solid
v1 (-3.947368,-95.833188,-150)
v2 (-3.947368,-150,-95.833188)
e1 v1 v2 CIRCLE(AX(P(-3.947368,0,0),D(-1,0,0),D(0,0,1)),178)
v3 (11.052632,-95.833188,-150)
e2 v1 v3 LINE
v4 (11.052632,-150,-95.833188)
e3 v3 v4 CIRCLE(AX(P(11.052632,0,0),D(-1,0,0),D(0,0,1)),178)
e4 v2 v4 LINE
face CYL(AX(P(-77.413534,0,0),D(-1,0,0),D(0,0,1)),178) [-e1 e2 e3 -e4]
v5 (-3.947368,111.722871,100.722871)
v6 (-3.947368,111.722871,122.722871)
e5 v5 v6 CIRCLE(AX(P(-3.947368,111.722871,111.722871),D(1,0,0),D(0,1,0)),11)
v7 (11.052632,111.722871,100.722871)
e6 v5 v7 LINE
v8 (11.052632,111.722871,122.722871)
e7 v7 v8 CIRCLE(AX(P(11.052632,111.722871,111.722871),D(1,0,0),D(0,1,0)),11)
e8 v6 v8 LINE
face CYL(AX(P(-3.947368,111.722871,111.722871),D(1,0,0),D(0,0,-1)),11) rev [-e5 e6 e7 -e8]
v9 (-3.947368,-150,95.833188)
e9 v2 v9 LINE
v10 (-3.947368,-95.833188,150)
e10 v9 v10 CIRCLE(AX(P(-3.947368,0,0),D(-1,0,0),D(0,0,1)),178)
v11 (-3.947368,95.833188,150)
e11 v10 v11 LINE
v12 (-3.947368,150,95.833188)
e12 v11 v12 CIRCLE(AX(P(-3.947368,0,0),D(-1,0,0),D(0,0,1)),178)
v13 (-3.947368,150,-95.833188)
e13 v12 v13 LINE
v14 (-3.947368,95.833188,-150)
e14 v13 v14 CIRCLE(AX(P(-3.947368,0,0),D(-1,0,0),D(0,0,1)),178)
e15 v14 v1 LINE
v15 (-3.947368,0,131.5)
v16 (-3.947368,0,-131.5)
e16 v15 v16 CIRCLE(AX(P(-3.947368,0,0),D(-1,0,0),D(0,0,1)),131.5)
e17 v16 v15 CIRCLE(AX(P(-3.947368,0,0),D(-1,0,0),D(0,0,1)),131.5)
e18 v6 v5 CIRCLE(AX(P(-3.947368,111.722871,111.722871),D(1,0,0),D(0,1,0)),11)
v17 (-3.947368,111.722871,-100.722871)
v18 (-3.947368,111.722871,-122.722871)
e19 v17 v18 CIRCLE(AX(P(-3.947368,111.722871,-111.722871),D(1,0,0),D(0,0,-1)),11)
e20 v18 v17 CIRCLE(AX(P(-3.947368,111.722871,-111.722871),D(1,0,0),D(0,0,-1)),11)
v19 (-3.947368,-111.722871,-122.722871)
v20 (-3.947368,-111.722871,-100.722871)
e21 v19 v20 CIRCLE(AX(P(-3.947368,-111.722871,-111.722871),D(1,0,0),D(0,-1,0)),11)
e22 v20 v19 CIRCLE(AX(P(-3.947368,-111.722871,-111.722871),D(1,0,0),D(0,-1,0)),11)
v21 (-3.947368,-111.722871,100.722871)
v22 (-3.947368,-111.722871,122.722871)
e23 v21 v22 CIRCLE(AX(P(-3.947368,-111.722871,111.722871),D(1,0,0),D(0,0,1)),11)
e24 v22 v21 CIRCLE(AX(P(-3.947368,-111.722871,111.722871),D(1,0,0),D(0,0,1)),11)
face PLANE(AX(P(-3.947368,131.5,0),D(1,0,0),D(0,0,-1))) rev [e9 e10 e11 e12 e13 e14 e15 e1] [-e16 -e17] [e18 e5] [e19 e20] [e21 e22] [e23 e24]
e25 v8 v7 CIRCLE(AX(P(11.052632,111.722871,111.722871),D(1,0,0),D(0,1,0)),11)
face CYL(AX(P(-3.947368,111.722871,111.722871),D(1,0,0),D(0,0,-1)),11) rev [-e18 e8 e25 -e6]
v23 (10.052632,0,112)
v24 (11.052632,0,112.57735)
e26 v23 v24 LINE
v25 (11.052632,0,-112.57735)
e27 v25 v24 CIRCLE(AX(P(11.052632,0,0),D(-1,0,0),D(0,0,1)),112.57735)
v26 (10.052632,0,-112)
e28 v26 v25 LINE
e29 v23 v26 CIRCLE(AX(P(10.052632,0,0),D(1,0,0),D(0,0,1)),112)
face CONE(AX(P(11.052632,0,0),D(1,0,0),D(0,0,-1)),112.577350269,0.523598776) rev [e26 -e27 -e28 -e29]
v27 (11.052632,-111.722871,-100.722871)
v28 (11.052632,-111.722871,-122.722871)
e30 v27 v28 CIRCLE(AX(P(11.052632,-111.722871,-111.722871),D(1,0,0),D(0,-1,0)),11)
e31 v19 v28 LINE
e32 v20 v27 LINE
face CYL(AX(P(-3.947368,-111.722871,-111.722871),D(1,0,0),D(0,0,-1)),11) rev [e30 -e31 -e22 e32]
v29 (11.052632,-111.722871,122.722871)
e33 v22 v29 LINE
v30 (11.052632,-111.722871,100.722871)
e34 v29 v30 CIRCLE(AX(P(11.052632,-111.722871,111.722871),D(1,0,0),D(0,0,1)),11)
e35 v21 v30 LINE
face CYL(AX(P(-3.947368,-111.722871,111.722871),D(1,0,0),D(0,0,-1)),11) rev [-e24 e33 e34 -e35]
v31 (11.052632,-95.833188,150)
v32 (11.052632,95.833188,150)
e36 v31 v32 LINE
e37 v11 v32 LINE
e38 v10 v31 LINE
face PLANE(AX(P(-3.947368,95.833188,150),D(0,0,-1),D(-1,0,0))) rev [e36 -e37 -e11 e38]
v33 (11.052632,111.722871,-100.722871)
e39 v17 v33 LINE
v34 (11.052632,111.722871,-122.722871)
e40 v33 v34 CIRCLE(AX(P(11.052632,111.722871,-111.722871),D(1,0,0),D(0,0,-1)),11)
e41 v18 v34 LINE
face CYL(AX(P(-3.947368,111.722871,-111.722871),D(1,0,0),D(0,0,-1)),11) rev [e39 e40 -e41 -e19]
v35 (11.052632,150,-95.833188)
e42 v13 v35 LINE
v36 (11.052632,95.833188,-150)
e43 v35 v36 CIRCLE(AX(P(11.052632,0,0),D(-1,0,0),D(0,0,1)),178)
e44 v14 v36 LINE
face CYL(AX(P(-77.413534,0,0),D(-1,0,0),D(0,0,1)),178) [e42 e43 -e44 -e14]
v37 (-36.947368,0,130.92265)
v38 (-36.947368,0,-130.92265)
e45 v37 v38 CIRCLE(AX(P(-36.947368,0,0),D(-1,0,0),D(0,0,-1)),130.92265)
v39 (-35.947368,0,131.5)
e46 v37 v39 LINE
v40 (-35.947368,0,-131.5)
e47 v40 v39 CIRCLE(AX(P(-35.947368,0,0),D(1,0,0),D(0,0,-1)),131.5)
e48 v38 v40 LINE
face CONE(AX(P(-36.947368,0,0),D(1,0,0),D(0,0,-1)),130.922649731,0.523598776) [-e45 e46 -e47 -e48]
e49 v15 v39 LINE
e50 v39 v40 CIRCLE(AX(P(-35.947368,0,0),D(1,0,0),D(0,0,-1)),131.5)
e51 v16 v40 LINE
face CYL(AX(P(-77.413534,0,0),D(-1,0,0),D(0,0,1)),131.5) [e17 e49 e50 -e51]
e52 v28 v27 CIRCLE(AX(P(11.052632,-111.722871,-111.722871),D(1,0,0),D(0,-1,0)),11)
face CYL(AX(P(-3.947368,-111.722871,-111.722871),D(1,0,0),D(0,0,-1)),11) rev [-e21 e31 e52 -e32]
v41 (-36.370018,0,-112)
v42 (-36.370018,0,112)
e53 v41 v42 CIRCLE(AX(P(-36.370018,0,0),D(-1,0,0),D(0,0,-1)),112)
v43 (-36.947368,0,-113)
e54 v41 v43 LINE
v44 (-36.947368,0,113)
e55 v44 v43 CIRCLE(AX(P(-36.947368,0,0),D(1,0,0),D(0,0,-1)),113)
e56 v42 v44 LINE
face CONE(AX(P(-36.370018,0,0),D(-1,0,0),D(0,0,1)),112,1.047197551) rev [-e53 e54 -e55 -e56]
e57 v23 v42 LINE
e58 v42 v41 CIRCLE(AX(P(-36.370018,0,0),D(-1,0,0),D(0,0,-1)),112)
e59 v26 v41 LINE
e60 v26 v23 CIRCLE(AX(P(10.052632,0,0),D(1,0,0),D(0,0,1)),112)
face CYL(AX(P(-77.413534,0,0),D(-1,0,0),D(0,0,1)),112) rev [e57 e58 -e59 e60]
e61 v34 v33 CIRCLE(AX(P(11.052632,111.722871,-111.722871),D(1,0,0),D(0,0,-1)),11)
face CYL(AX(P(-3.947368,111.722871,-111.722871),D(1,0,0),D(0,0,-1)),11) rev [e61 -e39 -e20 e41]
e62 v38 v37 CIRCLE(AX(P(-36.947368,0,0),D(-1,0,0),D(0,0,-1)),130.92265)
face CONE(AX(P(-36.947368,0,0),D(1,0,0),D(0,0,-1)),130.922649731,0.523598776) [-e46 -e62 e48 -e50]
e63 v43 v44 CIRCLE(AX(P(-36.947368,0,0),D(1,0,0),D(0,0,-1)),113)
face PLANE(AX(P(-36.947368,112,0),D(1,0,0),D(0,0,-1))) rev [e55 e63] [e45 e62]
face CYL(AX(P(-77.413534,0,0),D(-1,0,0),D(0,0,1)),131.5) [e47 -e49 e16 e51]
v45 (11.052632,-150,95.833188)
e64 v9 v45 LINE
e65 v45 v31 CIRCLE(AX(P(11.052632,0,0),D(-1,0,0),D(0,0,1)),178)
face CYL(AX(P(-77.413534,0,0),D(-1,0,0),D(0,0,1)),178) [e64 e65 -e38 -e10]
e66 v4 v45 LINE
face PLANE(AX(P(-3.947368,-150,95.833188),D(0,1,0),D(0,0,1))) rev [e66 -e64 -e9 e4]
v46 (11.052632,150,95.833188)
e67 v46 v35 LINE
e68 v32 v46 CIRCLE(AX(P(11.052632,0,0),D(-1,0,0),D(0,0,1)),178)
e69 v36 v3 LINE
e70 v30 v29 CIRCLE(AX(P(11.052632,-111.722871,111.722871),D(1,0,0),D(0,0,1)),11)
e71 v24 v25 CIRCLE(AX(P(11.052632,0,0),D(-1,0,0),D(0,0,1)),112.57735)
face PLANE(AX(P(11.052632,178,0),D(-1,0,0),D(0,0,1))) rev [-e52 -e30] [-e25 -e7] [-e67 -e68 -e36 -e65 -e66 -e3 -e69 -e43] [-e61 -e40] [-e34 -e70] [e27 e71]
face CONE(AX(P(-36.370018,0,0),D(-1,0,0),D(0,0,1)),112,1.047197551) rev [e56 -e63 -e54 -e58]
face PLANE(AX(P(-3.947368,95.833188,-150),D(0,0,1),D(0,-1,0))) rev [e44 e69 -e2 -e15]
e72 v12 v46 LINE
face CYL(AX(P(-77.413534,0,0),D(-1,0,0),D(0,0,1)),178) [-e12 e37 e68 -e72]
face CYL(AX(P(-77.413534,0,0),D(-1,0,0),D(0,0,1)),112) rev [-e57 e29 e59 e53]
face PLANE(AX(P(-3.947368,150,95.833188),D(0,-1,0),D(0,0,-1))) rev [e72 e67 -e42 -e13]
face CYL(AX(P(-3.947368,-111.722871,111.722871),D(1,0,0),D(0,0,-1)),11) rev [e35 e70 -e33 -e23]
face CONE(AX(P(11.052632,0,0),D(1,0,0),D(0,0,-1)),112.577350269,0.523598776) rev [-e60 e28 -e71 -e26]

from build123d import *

# Parameters (mm, degrees)
SKETCH2_R          = 11
CUT_EXTRUDE1_DEPTH = 15
CIRPATTERN1_COUNT  = 4
CUT_EXTRUDE2_DEPTH = 15
CHAMFER1_SIZE      = 1
CHAMFER1_SIZE2     = 0.577350269
CHAMFER2_SIZE      = 1
CHAMFER2_SIZE2     = 0.577350269
CHAMFER3_SIZE      = 1
CHAMFER3_SIZE2     = 0.577350269


with BuildPart() as part:
    # Sketch1 → Revolve1 (revolve)
    with BuildSketch(Plane.XY, mode=Mode.PRIVATE) as revolve1_sk:
        Polygon((-36.947368421, 131.5), (-3.947368421, 131.5), (-3.947368421, 178), (11.052631579, 178), (11.052631579, 112), (-36.947368421, 112), align=None)
    revolve(revolve1_sk.sketch.rotate(Axis((-77.413533835, 0, 0), (1, 0, 0)), 90), axis=Axis((-77.413533835, 0, 0), (1, 0, 0)))

    # Sketch2 → Cut-Extrude1 (cut)
    with BuildSketch(Plane(origin=(11.052631579, 0, 0), x_dir=(0, 0, -1), z_dir=(1, 0, 0))):
        with Locations((111.722871427, 111.722871427)):
            Circle(SKETCH2_R)
    cut_extrude1 = extrude(amount=-CUT_EXTRUDE1_DEPTH, mode=Mode.SUBTRACT)

    # CirPattern1: Cut-Extrude1 ×4 about axis
    cirpattern1_axis = Axis((0, 0, 0), (1, 0, 0))
    for i in range(1, CIRPATTERN1_COUNT):
        add(cut_extrude1.rotate(cirpattern1_axis, i * 360 / CIRPATTERN1_COUNT), mode=Mode.SUBTRACT)

    # Sketch3 → Cut-Extrude2 (cut)
    with BuildSketch(Plane(origin=(11.052631579, 0, 0), x_dir=(0, 0, -1), z_dir=(1, 0, 0))):
        with BuildLine():
            Line((-95.833188406, 150), (95.833188406, 150))
            ThreePointArc((95.833188406, 150), (0, 178), (-95.833188406, 150))
        make_face()
        with BuildLine():
            Line((-150, 95.833188406), (-150, -95.833188406))
            ThreePointArc((-150, -95.833188406), (-178, 0), (-150, 95.833188406))
        make_face()
        with BuildLine():
            Line((-95.833188406, -150), (95.833188406, -150))
            ThreePointArc((95.833188406, -150), (0, -178), (-95.833188406, -150))
        make_face()
        with BuildLine():
            Line((150, 95.833188406), (150, -95.833188406))
            ThreePointArc((150, -95.833188406), (178, 0), (150, 95.833188406))
        make_face()
    extrude(amount=-CUT_EXTRUDE2_DEPTH, mode=Mode.SUBTRACT)

    # Chamfer1
    chamfer1_edges = [part.edges().sort_by_distance(p)[0] for p in [
        (11.052631579, 0, -112),
    ]]
    chamfer1_side = [part.faces().sort_by_distance(p)[0] for p in [
        (-12.947368421, 0, -112),
    ]]
    chamfer(chamfer1_edges, length=CHAMFER1_SIZE, length2=CHAMFER1_SIZE2, reference=chamfer1_side[0])

    # Chamfer2
    chamfer2_edges = [part.edges().sort_by_distance(p)[0] for p in [
        (-36.947368421, 0, -112),
    ]]
    chamfer2_side = [part.faces().sort_by_distance(p)[0] for p in [
        (-36.947368421, 0, -115.719381669),
    ]]
    chamfer(chamfer2_edges, length=CHAMFER2_SIZE, length2=CHAMFER2_SIZE2, reference=chamfer2_side[0])

    # Chamfer3
    chamfer3_edges = [part.edges().sort_by_distance(p)[0] for p in [
        (-36.947368421, 0, -131.5),
    ]]
    chamfer3_side = [part.faces().sort_by_distance(p)[0] for p in [
        (-20.447368421, 0, -131.5),
    ]]
    chamfer(chamfer3_edges, length=CHAMFER3_SIZE, length2=CHAMFER3_SIZE2, reference=chamfer3_side[0])


solid = part.part
